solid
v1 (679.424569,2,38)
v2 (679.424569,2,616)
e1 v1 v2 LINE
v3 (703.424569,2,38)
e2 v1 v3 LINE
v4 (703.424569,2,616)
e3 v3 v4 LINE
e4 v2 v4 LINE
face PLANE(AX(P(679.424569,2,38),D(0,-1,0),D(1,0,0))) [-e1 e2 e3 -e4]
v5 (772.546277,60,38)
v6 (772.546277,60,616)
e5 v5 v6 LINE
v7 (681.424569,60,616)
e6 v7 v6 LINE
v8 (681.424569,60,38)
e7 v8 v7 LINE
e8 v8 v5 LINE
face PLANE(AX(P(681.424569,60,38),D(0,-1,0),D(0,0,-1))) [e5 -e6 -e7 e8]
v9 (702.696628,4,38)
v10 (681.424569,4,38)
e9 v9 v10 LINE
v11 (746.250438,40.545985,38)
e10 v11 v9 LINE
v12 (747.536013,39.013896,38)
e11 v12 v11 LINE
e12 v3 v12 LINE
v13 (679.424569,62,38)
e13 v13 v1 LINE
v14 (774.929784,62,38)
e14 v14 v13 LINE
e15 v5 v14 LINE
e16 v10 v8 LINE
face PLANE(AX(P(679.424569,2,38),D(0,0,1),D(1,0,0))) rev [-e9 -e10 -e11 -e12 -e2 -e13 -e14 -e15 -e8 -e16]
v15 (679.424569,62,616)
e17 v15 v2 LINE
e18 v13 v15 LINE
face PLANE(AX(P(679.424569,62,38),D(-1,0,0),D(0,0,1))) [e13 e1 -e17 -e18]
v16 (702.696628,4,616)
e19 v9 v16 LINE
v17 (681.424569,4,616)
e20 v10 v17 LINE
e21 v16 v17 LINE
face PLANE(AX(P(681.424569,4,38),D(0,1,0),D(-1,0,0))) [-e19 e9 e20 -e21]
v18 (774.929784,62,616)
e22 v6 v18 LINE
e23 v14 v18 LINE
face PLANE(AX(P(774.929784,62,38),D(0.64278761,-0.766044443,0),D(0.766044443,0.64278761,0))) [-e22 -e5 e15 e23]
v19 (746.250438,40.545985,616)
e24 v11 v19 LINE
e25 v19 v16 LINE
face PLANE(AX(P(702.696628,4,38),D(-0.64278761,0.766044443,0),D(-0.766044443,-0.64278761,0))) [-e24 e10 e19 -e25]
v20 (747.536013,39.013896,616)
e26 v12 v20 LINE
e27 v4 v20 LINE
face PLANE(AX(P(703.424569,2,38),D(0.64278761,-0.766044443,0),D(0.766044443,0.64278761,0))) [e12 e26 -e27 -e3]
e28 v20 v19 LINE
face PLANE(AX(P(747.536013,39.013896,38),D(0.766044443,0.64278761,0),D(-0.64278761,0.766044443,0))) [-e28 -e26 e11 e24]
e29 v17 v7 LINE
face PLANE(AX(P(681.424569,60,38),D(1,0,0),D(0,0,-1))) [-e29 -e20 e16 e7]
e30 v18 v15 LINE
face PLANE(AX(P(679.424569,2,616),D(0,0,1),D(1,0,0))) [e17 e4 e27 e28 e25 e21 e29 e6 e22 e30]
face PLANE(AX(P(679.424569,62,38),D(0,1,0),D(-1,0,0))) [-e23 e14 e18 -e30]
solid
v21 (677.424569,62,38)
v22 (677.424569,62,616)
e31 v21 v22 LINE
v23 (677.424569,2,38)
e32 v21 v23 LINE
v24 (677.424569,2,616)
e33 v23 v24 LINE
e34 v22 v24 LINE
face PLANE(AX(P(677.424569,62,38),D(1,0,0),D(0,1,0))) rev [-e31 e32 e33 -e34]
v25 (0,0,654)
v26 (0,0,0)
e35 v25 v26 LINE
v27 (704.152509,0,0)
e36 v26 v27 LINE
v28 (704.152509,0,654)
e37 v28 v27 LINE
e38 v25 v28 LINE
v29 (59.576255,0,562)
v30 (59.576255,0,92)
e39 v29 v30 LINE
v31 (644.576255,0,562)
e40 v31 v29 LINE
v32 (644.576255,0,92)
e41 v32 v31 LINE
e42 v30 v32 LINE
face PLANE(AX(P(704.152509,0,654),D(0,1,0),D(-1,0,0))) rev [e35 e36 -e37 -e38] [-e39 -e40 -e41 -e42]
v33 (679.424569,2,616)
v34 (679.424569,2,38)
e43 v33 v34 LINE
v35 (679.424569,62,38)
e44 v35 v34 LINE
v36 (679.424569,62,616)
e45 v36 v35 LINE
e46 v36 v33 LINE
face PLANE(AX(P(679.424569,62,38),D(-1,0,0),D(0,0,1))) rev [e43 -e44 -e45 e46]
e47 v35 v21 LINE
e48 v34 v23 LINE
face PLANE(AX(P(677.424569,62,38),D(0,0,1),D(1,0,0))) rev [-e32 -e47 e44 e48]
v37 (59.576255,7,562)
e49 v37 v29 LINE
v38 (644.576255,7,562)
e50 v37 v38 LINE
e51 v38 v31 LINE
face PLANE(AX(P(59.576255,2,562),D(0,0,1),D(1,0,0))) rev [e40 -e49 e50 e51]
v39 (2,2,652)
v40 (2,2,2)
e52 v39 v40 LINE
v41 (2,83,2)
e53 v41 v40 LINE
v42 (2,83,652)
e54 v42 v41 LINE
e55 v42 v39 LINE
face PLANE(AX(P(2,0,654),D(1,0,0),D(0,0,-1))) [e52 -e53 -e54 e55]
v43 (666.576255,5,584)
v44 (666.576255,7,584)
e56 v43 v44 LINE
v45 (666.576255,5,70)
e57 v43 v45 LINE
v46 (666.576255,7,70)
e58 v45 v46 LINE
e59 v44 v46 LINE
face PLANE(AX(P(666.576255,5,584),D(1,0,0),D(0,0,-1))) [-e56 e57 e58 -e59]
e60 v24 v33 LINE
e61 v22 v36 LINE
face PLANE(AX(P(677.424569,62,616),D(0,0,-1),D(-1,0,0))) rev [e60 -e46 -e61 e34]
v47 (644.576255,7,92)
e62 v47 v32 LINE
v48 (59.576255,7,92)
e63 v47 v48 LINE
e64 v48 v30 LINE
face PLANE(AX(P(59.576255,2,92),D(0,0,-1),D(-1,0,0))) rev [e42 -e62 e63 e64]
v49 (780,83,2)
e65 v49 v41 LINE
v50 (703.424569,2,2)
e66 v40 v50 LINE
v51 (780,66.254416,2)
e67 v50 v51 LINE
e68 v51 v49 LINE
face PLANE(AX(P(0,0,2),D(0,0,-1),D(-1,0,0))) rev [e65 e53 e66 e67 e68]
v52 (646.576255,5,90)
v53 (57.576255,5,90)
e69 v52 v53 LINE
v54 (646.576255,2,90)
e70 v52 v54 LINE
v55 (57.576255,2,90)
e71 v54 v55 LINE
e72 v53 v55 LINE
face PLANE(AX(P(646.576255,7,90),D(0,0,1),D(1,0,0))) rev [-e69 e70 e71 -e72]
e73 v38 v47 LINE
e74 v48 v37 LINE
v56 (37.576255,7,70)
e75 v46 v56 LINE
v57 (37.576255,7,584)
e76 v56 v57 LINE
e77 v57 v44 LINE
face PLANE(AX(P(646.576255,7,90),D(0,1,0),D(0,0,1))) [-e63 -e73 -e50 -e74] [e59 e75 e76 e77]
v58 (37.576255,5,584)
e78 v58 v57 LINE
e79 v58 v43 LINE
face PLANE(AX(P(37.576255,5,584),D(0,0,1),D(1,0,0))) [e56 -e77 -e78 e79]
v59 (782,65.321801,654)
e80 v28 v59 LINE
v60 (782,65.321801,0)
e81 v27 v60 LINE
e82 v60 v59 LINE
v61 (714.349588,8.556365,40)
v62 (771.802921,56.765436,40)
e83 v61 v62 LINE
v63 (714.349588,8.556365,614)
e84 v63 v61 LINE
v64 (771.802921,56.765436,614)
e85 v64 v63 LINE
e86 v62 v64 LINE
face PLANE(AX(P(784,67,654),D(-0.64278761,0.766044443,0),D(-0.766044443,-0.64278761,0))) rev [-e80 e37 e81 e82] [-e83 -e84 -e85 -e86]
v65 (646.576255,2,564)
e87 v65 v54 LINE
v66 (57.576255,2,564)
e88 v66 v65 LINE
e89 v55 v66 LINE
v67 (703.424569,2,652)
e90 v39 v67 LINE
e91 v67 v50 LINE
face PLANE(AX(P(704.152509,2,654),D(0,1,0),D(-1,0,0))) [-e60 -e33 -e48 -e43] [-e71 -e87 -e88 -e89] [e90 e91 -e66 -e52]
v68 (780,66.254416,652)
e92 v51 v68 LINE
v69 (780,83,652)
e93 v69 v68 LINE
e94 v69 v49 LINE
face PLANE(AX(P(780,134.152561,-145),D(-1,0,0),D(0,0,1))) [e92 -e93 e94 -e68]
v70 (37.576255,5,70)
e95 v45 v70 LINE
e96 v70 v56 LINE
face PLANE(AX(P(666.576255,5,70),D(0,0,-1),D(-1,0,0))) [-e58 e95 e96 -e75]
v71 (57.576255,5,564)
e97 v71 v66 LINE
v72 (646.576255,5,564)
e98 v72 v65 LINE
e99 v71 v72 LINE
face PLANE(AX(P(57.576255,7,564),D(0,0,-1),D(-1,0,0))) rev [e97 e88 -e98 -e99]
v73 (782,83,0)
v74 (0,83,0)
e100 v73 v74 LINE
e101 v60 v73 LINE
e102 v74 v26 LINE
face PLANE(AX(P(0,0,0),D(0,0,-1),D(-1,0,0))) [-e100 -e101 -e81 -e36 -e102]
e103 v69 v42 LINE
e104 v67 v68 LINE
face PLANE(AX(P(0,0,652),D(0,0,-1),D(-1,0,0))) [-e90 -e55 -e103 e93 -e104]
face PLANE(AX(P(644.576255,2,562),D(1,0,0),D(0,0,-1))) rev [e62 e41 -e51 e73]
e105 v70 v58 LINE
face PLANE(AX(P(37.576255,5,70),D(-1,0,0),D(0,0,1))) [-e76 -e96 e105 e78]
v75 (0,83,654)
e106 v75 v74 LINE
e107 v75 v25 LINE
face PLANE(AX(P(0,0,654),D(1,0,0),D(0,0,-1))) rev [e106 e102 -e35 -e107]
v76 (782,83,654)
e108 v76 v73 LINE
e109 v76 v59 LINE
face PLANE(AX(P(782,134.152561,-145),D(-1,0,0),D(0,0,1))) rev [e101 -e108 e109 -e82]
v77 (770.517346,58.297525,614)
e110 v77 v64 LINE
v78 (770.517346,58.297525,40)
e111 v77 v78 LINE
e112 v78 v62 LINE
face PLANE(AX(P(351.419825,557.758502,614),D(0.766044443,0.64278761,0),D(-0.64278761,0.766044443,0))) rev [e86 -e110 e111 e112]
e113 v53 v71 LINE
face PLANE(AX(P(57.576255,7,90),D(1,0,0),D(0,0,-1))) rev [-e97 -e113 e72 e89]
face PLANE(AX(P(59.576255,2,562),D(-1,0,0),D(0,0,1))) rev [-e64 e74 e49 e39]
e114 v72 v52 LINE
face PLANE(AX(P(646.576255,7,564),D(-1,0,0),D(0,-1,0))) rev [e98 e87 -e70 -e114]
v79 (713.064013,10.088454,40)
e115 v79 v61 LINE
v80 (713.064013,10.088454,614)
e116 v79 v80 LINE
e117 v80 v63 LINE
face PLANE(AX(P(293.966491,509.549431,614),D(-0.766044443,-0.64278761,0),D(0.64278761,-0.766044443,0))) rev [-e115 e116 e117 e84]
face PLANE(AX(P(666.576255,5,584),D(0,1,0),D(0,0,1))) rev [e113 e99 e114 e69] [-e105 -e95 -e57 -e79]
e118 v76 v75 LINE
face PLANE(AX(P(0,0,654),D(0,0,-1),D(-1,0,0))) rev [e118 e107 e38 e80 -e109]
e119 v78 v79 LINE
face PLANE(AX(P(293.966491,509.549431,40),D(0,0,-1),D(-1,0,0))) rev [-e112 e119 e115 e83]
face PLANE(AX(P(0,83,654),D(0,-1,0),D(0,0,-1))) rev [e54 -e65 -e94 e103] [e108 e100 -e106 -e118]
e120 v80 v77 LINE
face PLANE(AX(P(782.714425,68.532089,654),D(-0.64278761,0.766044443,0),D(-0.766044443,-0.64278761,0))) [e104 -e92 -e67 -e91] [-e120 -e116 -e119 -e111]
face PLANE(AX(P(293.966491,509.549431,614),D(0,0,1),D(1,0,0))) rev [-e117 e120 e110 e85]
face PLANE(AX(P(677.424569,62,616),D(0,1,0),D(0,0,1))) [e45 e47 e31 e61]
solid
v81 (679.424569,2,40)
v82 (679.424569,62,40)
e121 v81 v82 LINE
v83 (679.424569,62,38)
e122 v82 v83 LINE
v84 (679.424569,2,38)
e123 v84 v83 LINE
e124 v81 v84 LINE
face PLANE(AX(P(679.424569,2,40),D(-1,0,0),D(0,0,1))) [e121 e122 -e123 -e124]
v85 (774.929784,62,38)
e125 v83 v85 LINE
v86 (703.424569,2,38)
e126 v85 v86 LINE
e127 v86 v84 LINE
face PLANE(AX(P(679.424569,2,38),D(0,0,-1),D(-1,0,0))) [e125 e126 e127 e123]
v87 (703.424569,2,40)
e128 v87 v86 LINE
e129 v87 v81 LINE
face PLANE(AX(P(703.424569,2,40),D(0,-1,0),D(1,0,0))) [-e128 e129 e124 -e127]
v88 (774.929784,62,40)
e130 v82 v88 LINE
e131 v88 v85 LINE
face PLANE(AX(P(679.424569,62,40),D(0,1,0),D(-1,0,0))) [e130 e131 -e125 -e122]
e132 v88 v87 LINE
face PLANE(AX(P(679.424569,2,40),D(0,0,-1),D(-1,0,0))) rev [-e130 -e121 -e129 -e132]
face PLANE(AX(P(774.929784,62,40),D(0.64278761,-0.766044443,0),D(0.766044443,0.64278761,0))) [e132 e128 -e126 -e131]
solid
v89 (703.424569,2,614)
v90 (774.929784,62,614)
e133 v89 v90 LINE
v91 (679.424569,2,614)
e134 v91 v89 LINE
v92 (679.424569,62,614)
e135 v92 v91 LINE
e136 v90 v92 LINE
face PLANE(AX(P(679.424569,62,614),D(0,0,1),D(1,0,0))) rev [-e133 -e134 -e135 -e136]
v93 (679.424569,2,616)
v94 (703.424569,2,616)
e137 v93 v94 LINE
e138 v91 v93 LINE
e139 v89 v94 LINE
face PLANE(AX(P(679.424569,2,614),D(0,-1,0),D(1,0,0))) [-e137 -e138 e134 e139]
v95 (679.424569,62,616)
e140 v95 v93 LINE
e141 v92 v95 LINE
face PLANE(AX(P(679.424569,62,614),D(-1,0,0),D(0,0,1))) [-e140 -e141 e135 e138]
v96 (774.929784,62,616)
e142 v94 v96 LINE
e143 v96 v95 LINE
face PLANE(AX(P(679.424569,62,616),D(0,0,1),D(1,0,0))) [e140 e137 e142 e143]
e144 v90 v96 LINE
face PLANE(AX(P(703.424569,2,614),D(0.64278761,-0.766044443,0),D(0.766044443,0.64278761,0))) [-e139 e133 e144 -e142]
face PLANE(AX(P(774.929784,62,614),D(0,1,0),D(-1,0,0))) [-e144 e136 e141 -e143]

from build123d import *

# Parameters (mm, degrees)
EXTRUDE_1_DEPTH      = 654
SKETCH_8_W           = 110.00435438
SKETCH_8_H           = 134.15256119
CUT_EXTRUDE_2_DEPTH  = 799
SHELL_1_T            = -2
SKETCH_3_W           = 75
SKETCH_3_H           = 574
CUT_EXTRUDE_1_DEPTH  = 654
SKETCH_5_W           = 2
SKETCH_5_H           = 578
EXTRUDE_2_DEPTH      = 60
EXTRUDE_3_DEPTH      = 289
EXTRUDE_3_DEPTH_BACK = 289
EXTRUDE_5_DEPTH      = 2
EXTRUDE_6_DEPTH      = 2
SKETCH_11_W          = 585
SKETCH_11_H          = 470
CUT_EXTRUDE_3_DEPTH  = 2
SKETCH_12_W          = 589
SKETCH_12_H          = 474
SKETCH_12_W_2        = 585
SKETCH_12_H_2        = 470
EXTRUDE_7_DEPTH      = 5
SKETCH_15_W          = 629
SKETCH_15_H          = 514
SKETCH_15_W_2        = 585
SKETCH_15_H_2        = 470
EXTRUDE_8_DEPTH      = 2


with BuildPart() as part:
    # 草图2 → 凸台-拉伸1 (new body)
    with BuildSketch(Plane.XY):
        Polygon((0, 0), (0, 83), (784, 83), (784, 67), (704.152509296, 0), align=None)
    extrude(amount=EXTRUDE_1_DEPTH)

    # 草图8 → 切除-拉伸2 (cut)
    with BuildSketch(Plane.XY.offset(654)):
        with Locations((837.00217719, 67.076280595)):
            Rectangle(SKETCH_8_W, SKETCH_8_H)
    extrude(amount=-CUT_EXTRUDE_2_DEPTH, mode=Mode.SUBTRACT)

    # 抽壳1
    shell_1_openings = [part.faces().sort_by_distance(p)[0] for p in [
        (391, 83, 327),
    ]]
    offset(amount=SHELL_1_T, openings=shell_1_openings, kind=Kind.INTERSECTION)

    # 草图3 → 切除-拉伸1 (cut)
    with BuildSketch(Plane(origin=(290.938854629, -346.727425229, 0), x_dir=(0.7660444431189772, 0.6427876096865405, 0), z_dir=(0.6427876096865404, -0.7660444431189772, 0))):
        with Locations((590.223457765, 327)):
            Rectangle(SKETCH_3_W, SKETCH_3_H)
    extrude(amount=-CUT_EXTRUDE_1_DEPTH, mode=Mode.SUBTRACT)

    # 草图5 → 凸台-拉伸2 (add)
    with BuildSketch(Plane(origin=(0, 2, 0), x_dir=(1, 0, 0), z_dir=(0, 1, 0))):
        with Locations((678.424568828, -327)):
            Rectangle(SKETCH_5_W, SKETCH_5_H)
    extrude(amount=EXTRUDE_2_DEPTH)

    # 草图11 → 切除-拉伸3 (cut)
    with BuildSketch(Plane.XZ):
        with Locations((352.076254648, 327)):
            Rectangle(SKETCH_11_W, SKETCH_11_H)
    extrude(amount=-CUT_EXTRUDE_3_DEPTH, mode=Mode.SUBTRACT)

    # 草图12 → 凸台-拉伸7 (add)
    with BuildSketch(Plane(origin=(0, 2, 0), x_dir=(1, 0, 0), z_dir=(0, 1, 0))):
        with Locations((352.076254648, -327)):
            Rectangle(SKETCH_12_W, SKETCH_12_H)
        with Locations((352.076254648, -327)):
            Rectangle(SKETCH_12_W_2, SKETCH_12_H_2, mode=Mode.SUBTRACT)
    extrude(amount=EXTRUDE_7_DEPTH)

    # 草图15 → 凸台-拉伸8 (add)
    with BuildSketch(Plane(origin=(0, 7, 0), x_dir=(1, 0, 0), z_dir=(0, 1, 0))):
        with Locations((352.076254648, -327)):
            Rectangle(SKETCH_15_W, SKETCH_15_H)
        with Locations((352.076254648, -327)):
            Rectangle(SKETCH_15_W_2, SKETCH_15_H_2, mode=Mode.SUBTRACT)
    extrude(amount=-EXTRUDE_8_DEPTH)


with BuildPart() as body_2:
    # 草图6 → 凸台-拉伸3 (new, two sides: drawn at the far end of the back side and taken through both)
    with BuildSketch(Plane.XY.offset(327).offset(-EXTRUDE_3_DEPTH_BACK)):
        Polygon((679.424568828, 62), (774.929784383, 62), (772.546277198, 60), (681.424568828, 60), (681.424568828, 4), (702.696628359, 4), (746.250437533, 40.545985214), (747.536012752, 39.013896328), (703.424568828, 2), (679.424568828, 2), align=None)
    extrude(amount=EXTRUDE_3_DEPTH + EXTRUDE_3_DEPTH_BACK)


with BuildPart() as body_3:
    # 草图9 → 凸台-拉伸5 (new body)
    with BuildSketch(Plane.XY.offset(616)):
        Polygon((679.424568828, 62), (679.424568828, 2), (703.424568828, 2), (774.929784383, 62), align=None)
    extrude(amount=-EXTRUDE_5_DEPTH)


with BuildPart() as body_4:
    # 草图10 → 凸台-拉伸6 (new body)
    with BuildSketch(Plane(origin=(0, 0, 38), x_dir=(-1, 0, 0), z_dir=(0, 0, -1))):
        Polygon((-679.424568828, 2), (-679.424568828, 62), (-774.929784383, 62), (-703.424568828, 2), align=None)
    extrude(amount=-EXTRUDE_6_DEPTH)


solid = Compound([part.part, body_2.part, body_3.part, body_4.part])
